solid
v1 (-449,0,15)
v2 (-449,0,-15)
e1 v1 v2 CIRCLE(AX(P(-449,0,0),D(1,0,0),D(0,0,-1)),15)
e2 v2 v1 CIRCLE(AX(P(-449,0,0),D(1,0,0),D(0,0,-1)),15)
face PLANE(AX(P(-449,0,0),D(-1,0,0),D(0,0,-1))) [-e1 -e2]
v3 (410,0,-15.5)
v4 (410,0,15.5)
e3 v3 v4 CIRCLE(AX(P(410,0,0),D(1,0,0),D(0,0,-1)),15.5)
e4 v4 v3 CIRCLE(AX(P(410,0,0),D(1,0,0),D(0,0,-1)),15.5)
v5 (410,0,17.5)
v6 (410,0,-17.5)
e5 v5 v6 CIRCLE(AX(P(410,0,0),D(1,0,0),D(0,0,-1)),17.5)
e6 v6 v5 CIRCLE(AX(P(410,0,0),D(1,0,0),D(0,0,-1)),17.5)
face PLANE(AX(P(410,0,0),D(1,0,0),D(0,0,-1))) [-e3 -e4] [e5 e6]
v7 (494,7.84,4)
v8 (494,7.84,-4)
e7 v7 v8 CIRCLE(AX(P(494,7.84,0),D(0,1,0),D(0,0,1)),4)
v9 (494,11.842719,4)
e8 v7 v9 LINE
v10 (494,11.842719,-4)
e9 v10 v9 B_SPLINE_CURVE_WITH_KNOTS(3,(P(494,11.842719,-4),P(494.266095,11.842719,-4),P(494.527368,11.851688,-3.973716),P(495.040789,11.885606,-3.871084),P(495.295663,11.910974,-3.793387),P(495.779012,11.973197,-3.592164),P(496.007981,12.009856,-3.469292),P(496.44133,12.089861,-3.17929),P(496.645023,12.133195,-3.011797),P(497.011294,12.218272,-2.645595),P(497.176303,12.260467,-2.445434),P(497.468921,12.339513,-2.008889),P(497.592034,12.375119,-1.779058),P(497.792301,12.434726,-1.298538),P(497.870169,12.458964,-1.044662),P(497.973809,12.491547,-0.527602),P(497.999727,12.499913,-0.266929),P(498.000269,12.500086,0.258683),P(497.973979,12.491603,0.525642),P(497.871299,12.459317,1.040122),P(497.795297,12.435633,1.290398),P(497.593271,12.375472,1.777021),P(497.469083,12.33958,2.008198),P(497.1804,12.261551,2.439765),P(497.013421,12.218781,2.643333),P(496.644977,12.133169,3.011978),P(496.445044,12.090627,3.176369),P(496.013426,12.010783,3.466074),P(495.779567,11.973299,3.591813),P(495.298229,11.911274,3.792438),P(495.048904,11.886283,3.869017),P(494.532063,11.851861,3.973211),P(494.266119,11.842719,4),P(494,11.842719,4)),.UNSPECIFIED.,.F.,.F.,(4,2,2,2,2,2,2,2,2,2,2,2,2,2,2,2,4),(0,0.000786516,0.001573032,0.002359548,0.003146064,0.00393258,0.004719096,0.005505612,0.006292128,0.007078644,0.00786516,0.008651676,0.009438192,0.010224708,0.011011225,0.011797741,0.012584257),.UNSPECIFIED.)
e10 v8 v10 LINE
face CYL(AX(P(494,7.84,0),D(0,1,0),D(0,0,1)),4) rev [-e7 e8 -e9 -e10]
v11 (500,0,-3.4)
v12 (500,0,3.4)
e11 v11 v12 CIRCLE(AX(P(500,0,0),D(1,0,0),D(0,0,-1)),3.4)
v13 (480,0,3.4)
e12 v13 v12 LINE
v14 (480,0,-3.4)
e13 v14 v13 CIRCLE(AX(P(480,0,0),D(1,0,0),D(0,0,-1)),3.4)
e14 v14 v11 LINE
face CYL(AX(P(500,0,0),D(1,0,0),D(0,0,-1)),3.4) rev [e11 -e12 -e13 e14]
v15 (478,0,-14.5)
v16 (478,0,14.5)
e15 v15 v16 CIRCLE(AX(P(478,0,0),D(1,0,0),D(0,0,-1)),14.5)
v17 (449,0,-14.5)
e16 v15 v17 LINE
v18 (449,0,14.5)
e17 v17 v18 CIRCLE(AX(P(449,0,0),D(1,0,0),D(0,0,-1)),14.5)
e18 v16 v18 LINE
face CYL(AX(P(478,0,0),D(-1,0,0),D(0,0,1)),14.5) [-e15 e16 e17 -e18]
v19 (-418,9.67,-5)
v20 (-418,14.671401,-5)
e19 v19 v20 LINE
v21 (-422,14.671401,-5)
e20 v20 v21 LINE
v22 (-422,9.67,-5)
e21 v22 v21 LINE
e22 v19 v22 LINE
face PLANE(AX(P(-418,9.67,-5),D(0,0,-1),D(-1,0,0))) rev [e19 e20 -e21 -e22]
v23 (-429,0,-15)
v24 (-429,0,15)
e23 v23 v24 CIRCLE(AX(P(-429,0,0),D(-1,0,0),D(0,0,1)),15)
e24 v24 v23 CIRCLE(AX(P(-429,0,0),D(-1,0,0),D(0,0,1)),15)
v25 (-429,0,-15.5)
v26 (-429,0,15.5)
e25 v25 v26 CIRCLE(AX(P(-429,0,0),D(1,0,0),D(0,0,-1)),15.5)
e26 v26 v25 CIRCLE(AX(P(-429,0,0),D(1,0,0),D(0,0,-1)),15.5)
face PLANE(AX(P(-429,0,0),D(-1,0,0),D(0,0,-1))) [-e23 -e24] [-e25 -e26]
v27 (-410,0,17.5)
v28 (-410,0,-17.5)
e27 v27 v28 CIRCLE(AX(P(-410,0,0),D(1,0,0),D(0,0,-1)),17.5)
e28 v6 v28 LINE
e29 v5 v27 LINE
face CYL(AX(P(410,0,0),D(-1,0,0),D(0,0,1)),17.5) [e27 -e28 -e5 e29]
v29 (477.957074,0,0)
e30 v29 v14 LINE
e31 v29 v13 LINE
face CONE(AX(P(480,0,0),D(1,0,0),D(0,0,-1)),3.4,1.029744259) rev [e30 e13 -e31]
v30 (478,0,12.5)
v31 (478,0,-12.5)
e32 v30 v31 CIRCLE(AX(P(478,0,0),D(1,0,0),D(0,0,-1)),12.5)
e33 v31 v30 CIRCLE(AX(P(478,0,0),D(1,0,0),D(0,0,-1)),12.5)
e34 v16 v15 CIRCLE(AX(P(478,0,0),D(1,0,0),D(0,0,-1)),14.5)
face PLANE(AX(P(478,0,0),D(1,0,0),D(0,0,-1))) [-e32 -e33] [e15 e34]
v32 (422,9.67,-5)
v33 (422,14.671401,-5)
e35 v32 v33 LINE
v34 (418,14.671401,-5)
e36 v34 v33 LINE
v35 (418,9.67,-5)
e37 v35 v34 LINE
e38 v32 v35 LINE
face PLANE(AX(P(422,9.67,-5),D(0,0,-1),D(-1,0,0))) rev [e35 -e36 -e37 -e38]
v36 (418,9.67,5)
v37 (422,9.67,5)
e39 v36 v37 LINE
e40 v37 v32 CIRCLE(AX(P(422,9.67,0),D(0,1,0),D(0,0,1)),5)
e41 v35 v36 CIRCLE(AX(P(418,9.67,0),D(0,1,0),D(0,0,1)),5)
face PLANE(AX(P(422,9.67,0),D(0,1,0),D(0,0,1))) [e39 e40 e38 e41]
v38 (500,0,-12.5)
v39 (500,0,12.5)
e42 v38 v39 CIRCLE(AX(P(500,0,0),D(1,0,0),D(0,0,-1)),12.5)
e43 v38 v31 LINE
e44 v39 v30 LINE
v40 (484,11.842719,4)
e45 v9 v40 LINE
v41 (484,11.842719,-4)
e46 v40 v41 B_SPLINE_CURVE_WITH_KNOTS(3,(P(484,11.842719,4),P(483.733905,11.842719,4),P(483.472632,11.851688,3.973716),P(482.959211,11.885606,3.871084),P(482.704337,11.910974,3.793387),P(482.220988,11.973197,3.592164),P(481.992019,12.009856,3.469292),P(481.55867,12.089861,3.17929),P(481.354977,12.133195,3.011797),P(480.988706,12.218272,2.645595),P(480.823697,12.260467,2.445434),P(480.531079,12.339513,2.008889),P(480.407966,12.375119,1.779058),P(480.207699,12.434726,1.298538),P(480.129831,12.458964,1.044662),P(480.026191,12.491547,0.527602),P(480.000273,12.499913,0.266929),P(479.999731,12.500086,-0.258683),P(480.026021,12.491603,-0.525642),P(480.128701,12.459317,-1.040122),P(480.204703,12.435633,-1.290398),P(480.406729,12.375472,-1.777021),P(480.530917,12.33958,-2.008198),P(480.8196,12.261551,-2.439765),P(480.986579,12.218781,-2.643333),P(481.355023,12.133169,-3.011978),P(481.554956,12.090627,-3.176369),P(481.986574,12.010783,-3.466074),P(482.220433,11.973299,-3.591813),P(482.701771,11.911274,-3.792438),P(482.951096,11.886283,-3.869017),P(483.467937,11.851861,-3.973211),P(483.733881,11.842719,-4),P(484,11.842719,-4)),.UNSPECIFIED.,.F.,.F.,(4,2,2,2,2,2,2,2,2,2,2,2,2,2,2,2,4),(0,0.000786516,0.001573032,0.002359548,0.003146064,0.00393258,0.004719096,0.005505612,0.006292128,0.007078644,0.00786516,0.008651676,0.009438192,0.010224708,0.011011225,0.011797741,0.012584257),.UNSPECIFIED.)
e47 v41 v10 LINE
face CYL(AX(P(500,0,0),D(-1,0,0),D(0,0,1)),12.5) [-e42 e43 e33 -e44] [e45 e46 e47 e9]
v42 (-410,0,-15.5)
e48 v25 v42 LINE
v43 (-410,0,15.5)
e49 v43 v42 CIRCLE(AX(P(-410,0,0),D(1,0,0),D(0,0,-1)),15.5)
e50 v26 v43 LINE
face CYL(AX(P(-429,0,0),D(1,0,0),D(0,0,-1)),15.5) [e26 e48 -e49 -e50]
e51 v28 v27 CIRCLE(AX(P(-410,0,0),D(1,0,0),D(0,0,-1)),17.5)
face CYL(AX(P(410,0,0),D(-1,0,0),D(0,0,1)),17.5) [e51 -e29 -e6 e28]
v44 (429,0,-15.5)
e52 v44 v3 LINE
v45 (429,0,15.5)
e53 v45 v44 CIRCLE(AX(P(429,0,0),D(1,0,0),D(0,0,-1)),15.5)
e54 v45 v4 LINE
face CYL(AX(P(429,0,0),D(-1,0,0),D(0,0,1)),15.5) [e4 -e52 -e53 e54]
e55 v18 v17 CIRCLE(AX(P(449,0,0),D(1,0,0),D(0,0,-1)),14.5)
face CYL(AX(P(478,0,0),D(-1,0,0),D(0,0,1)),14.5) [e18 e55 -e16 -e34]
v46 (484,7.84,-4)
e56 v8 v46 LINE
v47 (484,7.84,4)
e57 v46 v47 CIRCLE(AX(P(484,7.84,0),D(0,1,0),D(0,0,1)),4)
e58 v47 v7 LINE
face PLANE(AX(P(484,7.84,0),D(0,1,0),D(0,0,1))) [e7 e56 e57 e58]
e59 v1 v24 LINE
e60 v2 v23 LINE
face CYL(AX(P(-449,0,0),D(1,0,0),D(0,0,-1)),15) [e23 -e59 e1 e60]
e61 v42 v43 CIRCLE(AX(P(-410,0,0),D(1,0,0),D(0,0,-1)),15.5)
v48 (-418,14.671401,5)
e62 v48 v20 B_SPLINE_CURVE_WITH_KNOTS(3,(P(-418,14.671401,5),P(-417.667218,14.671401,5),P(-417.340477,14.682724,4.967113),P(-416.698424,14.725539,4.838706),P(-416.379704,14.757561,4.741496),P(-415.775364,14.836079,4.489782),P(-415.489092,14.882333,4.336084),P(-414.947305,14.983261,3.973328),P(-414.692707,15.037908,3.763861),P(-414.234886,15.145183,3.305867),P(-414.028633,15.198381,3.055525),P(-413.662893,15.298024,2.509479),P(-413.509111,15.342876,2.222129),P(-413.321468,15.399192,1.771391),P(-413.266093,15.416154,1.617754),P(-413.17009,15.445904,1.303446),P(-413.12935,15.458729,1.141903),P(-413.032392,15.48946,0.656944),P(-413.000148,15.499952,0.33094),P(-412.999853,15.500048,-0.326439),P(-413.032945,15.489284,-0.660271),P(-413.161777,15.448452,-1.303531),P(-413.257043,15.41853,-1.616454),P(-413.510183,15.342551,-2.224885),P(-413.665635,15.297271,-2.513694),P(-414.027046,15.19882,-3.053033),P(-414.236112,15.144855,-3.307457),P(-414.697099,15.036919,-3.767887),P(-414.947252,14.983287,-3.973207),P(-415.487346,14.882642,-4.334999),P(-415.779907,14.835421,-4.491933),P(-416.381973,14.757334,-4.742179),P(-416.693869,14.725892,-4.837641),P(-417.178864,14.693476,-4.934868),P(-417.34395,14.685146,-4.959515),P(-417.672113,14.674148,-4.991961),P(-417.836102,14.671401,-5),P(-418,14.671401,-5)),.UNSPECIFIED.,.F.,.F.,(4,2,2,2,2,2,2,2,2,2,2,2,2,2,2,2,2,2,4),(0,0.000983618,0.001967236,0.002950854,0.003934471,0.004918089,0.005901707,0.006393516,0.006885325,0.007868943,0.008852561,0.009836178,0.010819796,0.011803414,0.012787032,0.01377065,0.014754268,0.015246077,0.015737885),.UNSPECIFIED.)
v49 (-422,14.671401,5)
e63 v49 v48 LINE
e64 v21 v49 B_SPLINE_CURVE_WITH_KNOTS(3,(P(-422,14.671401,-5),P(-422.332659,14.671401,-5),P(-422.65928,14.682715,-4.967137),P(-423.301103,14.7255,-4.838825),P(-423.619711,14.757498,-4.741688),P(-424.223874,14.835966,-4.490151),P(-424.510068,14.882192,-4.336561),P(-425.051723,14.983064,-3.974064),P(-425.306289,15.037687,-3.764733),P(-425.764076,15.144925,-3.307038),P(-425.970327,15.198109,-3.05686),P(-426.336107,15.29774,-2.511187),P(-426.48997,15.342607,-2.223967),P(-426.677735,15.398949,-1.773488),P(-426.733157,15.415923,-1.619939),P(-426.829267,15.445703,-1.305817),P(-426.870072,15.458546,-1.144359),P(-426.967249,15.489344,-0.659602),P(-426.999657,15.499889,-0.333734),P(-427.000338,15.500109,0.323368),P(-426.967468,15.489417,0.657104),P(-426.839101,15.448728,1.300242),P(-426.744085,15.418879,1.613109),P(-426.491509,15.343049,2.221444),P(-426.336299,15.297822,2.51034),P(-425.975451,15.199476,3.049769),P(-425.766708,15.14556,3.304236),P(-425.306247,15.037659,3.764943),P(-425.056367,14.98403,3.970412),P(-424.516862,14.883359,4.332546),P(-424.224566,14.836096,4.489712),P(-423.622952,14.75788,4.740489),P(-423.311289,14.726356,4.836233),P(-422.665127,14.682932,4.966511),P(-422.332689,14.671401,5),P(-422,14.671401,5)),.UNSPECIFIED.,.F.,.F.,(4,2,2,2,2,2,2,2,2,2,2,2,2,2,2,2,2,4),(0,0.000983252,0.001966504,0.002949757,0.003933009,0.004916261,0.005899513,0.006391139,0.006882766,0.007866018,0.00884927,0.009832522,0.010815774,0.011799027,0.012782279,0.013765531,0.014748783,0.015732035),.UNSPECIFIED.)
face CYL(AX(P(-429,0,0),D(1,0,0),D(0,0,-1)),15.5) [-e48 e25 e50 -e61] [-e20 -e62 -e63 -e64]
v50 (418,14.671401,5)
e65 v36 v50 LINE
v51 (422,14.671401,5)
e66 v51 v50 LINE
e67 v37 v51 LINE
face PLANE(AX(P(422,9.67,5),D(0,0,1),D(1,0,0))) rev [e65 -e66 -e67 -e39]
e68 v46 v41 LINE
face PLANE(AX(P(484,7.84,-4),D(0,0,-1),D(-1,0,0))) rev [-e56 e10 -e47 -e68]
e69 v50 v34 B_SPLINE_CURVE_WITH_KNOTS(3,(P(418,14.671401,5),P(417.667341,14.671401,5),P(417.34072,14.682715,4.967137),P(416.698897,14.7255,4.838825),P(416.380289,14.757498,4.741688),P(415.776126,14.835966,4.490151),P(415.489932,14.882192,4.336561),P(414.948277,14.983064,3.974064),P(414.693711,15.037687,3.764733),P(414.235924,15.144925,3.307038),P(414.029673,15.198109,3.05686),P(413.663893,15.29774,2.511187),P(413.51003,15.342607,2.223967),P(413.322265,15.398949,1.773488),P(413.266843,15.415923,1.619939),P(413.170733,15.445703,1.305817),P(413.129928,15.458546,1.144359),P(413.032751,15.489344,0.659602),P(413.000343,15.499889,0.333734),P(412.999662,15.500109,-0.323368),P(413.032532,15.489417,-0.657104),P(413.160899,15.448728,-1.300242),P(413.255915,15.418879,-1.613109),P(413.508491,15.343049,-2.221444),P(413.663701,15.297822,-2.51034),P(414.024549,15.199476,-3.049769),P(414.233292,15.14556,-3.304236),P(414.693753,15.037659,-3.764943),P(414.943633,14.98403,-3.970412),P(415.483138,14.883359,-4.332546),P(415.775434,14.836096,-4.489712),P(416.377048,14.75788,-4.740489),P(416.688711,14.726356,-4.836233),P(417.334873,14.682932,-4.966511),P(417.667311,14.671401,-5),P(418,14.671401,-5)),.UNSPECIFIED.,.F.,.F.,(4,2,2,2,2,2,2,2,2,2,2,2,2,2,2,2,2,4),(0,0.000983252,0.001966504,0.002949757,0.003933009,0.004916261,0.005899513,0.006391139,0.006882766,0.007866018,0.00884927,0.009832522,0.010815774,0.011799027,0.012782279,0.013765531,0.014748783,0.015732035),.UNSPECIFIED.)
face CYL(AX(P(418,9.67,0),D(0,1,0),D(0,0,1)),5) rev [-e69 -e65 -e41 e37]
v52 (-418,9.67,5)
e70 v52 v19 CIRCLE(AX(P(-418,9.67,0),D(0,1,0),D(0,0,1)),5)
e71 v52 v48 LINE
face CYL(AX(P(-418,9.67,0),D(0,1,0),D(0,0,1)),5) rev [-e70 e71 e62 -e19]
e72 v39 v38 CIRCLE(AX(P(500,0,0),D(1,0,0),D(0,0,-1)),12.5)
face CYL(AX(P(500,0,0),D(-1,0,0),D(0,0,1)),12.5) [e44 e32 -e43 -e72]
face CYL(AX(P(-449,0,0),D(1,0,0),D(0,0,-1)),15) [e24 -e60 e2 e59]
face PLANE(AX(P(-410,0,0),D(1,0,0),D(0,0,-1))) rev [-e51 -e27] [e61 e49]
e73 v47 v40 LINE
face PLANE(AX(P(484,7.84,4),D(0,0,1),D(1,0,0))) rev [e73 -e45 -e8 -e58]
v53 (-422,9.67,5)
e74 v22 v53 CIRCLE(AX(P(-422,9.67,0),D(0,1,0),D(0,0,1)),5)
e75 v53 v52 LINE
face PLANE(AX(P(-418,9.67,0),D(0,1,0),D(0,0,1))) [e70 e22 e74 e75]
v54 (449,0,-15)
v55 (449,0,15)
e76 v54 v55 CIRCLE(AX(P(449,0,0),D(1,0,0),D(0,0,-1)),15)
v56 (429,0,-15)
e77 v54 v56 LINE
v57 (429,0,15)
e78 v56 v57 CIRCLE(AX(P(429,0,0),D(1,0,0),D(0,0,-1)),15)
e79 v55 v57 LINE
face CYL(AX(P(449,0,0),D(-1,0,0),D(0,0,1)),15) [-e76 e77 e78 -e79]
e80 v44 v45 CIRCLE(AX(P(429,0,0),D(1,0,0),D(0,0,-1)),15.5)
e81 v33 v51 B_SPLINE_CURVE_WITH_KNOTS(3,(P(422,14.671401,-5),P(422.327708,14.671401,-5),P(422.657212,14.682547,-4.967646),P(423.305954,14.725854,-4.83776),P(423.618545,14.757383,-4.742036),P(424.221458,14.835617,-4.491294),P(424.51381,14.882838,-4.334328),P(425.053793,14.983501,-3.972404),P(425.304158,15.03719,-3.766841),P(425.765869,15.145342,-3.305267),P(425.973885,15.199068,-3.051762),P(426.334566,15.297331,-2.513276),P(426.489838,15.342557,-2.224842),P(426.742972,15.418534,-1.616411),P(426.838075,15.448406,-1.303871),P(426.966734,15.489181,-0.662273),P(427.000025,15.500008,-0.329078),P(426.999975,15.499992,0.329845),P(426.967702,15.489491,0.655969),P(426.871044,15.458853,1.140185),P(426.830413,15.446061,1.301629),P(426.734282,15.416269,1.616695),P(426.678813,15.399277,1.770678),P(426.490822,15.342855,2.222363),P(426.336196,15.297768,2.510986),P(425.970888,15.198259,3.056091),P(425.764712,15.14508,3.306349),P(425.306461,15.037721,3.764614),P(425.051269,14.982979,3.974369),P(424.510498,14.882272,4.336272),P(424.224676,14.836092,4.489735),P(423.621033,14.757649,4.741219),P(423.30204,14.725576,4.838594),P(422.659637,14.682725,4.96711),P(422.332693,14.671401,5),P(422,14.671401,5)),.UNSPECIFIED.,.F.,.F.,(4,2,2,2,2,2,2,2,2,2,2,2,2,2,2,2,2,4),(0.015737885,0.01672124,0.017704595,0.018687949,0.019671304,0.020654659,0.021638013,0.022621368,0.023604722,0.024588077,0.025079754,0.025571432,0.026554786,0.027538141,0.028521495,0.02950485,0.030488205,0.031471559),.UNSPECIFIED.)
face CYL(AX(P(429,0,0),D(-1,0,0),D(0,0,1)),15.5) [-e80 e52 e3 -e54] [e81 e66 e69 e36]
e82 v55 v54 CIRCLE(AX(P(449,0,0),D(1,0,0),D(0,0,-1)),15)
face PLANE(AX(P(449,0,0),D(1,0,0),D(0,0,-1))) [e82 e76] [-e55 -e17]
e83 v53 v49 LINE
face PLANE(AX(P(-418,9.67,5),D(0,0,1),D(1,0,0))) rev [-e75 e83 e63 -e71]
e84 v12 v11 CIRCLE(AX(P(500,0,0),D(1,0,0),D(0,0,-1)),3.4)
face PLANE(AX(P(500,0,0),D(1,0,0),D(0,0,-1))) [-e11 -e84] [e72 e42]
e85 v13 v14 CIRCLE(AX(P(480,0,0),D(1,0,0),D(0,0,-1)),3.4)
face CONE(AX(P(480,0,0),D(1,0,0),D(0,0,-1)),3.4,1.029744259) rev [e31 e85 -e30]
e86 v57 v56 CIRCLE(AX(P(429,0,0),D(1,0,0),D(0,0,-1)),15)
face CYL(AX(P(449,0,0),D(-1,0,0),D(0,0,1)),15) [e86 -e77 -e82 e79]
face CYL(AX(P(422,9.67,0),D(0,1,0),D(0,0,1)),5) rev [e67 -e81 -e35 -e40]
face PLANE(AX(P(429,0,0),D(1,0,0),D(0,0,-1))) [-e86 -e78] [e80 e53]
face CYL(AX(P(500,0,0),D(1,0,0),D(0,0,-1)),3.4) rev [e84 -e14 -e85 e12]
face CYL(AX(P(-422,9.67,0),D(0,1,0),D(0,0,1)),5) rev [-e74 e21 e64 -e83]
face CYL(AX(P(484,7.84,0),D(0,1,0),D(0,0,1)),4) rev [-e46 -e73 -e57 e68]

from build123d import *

# Parameters (mm, degrees)
SKETCH_1_R             = 17.5
EXTRUDE_1_DEPTH        = 410
SKETCH_2_R             = 15.5
EXTRUDE_2_DEPTH        = 19
SKETCH_3_R             = 15
EXTRUDE_3_DEPTH        = 20
SKETCH_4_R             = 14.5
EXTRUDE_4_DEPTH        = 29
SKETCH_5_R             = 12.5
EXTRUDE_5_DEPTH        = 22
CUT_EXTRUDE_1_DEPTH    = 5.83
CUT_EXTRUDE_2_DEPTH    = 7.66
HOLE_WIZARD_M8_1_D     = 6.8
HOLE_WIZARD_M8_1_DEPTH = 20
HOLE_WIZARD_M8_1_TIP   = 2.042926105


with BuildPart() as part:
    # 草图1 → 凸台-拉伸1 (new, symmetric)
    with BuildSketch(Plane(origin=(0, 0, 0), x_dir=(0, 0, -1), z_dir=(1, 0, 0))):
        with Locations(Location((0, 0, 0), (0, 0, 180))):
            Circle(SKETCH_1_R)
    extrude(amount=EXTRUDE_1_DEPTH, both=True)

    # 草图2 → 凸台-拉伸2 (add)
    with BuildSketch(Plane(origin=(410, 0, 0), x_dir=(0, 0, -1), z_dir=(1, 0, 0))):
        Circle(SKETCH_2_R)
    extrude_2 = extrude(amount=EXTRUDE_2_DEPTH)

    # 草图3 → 凸台-拉伸3 (add)
    with BuildSketch(Plane(origin=(429, 0, 0), x_dir=(0, 0, -1), z_dir=(1, 0, 0))):
        Circle(SKETCH_3_R)
    extrude_3 = extrude(amount=EXTRUDE_3_DEPTH)

    # 草图4 → 凸台-拉伸4 (add)
    with BuildSketch(Plane(origin=(449, 0, 0), x_dir=(0, 0, -1), z_dir=(1, 0, 0))):
        with Locations(Location((0, 0, 0), (0, 0, 180))):
            Circle(SKETCH_4_R)
    extrude(amount=EXTRUDE_4_DEPTH)

    # 草图5 → 凸台-拉伸5 (add)
    with BuildSketch(Plane(origin=(478, 0, 0), x_dir=(0, 0, -1), z_dir=(1, 0, 0))):
        Circle(SKETCH_5_R)
    extrude(amount=EXTRUDE_5_DEPTH)

    # 镜向1: 凸台-拉伸2, 凸台-拉伸3 across plane
    add(extrude_2.mirror(Plane(origin=(0, 0, 0), x_dir=(0, 0, 1), z_dir=(1, 0, 0))))
    add(extrude_3.mirror(Plane(origin=(0, 0, 0), x_dir=(0, 0, 1), z_dir=(1, 0, 0))))

    # 草图6 → 切除-拉伸1 (cut)
    with BuildSketch(Plane(origin=(0, 15.5, 0), x_dir=(1, 0, 0), z_dir=(0, 1, 0))):
        with BuildLine():
            Line((-418, -5), (-422, -5))
            ThreePointArc((-422, -5), (-427, 0), (-422, 5))
            Line((-422, 5), (-418, 5))
            ThreePointArc((-418, 5), (-413, 0), (-418, -5))
        make_face()
        with BuildLine():
            Line((422, -5), (418, -5))
            ThreePointArc((418, -5), (413, 0), (418, 5))
            Line((418, 5), (422, 5))
            ThreePointArc((422, 5), (427, 0), (422, -5))
        make_face()
    extrude(amount=-CUT_EXTRUDE_1_DEPTH, mode=Mode.SUBTRACT)

    # 草图7 → 切除-拉伸2 (cut)
    with BuildSketch(Plane(origin=(0, 15.5, 0), x_dir=(1, 0, 0), z_dir=(0, 1, 0))):
        with BuildLine():
            Line((484, 4), (494, 4))
            ThreePointArc((494, 4), (498, 0), (494, -4))
            Line((494, -4), (484, -4))
            ThreePointArc((484, -4), (480, 0), (484, 4))
        make_face()
    extrude(amount=-CUT_EXTRUDE_2_DEPTH, mode=Mode.SUBTRACT)

    # M8 螺纹孔1
    with Locations(Plane(origin=(500, 0, 0), x_dir=(0, 0, -1), z_dir=(1, 0, 0))):
        with Locations((0, 0)):
            Hole(HOLE_WIZARD_M8_1_D / 2, depth=HOLE_WIZARD_M8_1_DEPTH)
            with Locations((0, 0, -(HOLE_WIZARD_M8_1_DEPTH + HOLE_WIZARD_M8_1_TIP / 2))):  # 118° drill point
                Cone(0, HOLE_WIZARD_M8_1_D / 2, HOLE_WIZARD_M8_1_TIP, mode=Mode.SUBTRACT)


solid = part.part
